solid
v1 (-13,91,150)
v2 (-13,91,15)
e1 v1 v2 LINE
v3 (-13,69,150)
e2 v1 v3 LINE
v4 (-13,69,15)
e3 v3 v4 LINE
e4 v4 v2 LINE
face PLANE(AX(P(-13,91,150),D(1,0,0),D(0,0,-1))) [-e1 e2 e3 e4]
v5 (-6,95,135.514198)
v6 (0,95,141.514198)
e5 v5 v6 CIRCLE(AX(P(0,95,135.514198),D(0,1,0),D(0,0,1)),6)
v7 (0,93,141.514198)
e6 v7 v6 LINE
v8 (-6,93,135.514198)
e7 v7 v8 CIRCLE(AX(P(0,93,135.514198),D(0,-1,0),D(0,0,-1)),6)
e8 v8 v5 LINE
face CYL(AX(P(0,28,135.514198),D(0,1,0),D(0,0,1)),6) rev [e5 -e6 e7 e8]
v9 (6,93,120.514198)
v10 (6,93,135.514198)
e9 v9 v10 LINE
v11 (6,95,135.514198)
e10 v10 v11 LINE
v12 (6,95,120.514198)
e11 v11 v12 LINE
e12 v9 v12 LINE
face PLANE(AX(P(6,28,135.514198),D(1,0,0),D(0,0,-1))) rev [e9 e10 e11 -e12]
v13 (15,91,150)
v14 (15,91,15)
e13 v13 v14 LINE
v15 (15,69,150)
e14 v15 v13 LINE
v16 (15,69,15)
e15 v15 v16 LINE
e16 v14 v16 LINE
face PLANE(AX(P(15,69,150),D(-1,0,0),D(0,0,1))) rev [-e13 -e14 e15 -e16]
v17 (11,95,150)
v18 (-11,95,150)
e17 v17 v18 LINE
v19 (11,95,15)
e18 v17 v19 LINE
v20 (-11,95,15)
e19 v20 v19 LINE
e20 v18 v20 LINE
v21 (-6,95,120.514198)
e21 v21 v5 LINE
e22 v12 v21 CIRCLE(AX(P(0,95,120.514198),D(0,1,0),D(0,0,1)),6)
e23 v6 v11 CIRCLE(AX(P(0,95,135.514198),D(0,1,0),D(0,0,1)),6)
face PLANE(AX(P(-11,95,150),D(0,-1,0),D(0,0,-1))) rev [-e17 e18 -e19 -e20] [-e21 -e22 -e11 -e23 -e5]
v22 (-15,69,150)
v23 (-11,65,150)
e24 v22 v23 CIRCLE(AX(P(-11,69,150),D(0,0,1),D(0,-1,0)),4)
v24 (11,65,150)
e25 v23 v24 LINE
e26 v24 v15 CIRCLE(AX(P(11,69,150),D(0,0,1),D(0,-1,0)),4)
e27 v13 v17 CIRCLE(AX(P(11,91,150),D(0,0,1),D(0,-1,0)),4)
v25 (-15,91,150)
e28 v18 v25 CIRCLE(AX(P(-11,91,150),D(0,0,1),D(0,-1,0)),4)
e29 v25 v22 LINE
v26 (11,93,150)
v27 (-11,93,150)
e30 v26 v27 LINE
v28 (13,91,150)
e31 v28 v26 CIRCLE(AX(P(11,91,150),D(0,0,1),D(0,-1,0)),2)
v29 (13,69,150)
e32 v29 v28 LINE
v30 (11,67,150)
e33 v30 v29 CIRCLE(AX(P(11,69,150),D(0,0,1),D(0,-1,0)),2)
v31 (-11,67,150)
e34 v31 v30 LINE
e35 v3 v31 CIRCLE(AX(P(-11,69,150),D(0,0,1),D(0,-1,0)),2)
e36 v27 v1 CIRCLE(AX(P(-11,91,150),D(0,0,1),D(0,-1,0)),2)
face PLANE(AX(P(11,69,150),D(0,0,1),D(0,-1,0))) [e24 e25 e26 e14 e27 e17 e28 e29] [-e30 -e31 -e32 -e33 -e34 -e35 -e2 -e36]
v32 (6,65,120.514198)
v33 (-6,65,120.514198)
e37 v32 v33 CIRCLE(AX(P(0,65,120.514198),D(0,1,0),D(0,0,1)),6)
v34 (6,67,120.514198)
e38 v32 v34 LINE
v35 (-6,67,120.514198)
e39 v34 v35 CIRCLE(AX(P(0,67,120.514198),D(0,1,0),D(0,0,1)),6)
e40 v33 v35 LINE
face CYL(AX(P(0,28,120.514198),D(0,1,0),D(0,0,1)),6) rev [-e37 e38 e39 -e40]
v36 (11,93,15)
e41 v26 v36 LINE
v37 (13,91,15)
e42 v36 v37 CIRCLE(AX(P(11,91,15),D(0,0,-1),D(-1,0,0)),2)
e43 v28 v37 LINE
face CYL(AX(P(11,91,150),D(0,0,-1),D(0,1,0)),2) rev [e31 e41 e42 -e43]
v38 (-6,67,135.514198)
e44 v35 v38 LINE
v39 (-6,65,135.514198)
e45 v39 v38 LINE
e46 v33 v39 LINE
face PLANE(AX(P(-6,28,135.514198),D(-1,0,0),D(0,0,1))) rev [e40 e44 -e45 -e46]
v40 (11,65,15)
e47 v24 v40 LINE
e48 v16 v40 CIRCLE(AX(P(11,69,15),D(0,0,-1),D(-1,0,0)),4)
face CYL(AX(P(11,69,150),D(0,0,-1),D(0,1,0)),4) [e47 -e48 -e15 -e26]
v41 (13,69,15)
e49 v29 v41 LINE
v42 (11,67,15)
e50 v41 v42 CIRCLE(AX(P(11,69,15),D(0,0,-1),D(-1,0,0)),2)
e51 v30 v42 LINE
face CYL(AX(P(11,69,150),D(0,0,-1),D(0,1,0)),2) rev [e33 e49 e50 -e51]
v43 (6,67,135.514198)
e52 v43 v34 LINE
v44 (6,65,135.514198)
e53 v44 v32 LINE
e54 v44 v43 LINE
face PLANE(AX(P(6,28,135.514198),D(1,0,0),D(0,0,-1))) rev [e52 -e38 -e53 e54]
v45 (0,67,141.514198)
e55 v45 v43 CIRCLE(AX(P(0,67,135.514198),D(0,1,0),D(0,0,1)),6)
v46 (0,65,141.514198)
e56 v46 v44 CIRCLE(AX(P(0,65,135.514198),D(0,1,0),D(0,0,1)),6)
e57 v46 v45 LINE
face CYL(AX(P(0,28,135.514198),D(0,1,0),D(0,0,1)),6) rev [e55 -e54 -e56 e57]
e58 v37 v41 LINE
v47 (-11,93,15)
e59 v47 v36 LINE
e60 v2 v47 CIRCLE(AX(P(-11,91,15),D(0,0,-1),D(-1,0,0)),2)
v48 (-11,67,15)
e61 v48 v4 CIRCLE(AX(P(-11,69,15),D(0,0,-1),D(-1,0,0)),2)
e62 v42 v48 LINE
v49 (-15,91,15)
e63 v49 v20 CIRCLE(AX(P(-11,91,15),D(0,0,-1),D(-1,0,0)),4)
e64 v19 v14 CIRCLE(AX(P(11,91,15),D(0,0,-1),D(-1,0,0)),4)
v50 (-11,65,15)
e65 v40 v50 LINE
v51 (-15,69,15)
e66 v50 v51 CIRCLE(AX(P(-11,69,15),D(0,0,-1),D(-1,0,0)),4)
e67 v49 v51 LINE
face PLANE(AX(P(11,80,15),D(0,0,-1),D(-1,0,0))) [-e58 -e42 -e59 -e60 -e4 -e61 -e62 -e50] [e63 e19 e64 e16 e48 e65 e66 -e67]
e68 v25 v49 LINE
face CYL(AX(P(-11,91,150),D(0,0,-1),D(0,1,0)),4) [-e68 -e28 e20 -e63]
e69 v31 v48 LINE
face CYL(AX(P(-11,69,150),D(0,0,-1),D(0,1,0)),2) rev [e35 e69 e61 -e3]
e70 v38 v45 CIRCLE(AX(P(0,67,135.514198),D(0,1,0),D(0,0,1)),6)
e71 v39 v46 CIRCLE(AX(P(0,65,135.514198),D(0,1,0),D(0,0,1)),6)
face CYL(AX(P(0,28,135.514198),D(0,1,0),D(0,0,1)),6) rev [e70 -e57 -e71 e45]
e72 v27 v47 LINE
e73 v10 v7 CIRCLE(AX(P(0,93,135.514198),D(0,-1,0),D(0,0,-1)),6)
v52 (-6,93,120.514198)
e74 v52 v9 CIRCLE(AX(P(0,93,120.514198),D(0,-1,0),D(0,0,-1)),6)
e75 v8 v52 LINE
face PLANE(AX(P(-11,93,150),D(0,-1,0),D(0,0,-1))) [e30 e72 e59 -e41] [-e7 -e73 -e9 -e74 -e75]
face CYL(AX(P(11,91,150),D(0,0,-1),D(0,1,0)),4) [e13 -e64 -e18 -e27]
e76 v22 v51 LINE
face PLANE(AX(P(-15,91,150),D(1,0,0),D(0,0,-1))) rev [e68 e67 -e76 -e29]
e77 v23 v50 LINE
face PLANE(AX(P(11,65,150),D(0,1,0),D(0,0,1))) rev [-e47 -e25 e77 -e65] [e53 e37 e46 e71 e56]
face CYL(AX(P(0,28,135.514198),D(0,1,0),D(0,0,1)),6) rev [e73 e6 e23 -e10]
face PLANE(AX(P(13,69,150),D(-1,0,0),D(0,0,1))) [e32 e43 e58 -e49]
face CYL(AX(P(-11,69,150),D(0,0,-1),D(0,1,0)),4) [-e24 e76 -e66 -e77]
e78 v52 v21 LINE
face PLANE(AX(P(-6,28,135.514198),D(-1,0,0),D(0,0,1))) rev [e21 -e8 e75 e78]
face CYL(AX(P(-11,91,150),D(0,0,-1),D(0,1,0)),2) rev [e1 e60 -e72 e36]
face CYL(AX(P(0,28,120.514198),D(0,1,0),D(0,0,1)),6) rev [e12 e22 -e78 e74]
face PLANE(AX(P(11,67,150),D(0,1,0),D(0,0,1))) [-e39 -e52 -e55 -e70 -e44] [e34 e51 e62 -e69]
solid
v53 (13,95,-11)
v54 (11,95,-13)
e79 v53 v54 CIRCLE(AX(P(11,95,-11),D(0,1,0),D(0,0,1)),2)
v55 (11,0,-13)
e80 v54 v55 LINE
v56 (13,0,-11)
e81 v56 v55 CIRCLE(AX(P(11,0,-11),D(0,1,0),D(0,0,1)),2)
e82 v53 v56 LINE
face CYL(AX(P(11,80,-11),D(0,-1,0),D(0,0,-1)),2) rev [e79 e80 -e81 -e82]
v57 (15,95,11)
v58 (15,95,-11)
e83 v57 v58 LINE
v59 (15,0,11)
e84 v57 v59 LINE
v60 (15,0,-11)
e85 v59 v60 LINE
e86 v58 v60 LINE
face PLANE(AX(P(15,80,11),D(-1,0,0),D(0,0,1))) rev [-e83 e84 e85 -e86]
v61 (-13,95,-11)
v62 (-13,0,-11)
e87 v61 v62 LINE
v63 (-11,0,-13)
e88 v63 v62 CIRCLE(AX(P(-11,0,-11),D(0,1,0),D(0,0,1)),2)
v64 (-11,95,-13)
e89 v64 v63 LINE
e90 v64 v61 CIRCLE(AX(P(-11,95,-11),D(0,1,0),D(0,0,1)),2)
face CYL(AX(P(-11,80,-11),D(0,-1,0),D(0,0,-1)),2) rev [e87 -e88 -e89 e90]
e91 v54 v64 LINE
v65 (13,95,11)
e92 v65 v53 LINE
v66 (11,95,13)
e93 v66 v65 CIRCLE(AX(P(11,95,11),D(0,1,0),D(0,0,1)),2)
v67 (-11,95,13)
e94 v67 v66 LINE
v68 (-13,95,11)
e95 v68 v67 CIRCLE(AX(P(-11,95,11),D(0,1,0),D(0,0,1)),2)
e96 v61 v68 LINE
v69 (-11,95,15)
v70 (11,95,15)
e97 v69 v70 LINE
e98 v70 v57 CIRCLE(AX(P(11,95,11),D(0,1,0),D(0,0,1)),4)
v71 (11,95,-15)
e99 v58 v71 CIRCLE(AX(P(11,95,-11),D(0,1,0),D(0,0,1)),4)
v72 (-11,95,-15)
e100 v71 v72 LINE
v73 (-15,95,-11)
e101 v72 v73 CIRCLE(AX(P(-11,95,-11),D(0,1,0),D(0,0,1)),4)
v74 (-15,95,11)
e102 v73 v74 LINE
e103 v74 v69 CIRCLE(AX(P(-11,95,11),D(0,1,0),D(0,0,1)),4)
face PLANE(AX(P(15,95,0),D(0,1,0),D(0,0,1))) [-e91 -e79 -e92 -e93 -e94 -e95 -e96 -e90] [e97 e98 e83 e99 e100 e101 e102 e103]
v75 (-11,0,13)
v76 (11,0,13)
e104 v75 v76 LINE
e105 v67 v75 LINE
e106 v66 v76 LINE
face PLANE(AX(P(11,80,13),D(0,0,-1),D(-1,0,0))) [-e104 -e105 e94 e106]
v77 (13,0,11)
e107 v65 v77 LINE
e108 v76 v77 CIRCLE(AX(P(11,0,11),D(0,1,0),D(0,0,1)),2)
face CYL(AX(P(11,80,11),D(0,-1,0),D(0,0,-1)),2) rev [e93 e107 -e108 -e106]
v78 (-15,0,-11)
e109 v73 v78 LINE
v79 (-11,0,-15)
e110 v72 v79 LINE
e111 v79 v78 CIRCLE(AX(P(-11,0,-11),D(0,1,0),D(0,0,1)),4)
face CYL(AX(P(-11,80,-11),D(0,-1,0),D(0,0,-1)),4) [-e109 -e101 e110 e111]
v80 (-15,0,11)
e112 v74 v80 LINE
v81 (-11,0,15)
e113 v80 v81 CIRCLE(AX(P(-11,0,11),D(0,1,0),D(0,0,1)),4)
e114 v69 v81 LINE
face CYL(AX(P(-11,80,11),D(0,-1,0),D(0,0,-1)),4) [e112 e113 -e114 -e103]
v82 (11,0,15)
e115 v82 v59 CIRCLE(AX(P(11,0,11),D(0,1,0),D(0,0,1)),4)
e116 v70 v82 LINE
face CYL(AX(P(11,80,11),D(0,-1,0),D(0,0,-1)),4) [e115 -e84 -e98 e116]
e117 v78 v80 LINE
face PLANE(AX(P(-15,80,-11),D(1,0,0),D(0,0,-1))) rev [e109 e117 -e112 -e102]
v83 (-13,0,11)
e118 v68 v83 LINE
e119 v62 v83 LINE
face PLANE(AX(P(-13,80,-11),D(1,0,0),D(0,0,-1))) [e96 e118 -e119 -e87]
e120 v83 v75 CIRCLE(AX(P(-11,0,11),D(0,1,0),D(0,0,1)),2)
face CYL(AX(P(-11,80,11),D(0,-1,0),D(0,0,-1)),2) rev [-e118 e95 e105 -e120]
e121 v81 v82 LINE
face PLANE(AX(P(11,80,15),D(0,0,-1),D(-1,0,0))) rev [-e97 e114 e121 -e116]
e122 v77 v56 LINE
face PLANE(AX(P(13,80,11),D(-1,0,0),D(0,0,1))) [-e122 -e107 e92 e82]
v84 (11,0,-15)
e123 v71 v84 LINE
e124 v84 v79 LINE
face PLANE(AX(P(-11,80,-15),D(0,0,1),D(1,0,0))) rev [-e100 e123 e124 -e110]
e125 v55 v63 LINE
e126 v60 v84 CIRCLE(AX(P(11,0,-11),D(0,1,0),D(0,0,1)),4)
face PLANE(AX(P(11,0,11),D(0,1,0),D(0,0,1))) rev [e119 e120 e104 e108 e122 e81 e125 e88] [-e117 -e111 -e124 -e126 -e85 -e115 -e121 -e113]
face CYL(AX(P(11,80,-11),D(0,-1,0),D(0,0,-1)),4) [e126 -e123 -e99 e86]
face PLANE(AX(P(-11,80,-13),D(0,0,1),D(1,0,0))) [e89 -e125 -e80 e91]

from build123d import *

# Parameters (mm, degrees)
GB_6728_1986_030_X_30_X_2_1_DEPTH        = 95
GB_6728_1986_030_X_30_X_2_1_2_DEPTH      = 150
GB_6728_1986_030_X_30_X_2_1_2_DEPTH_BACK = 1
CUT_EXTRUDE_1_DEPTH                      = 67


with BuildPart() as part:
    # Sketch13 on segment 1 (carried to segment 1) → Gb／6728-1986方形空心型钢 030 X 30 X 2(1) (new body)
    with BuildSketch(Plane.ZX):
        with BuildLine():
            Line((-11, -15), (11, -15))
            ThreePointArc((11, -15), (13.828427125, -13.828427125), (15, -11))
            Line((15, -11), (15, 11))
            ThreePointArc((15, 11), (13.828427125, 13.828427125), (11, 15))
            Line((11, 15), (-11, 15))
            ThreePointArc((-11, 15), (-13.828427125, 13.828427125), (-15, 11))
            Line((-15, 11), (-15, -11))
            ThreePointArc((-15, -11), (-13.828427125, -13.828427125), (-11, -15))
        make_face()
        with BuildLine():
            Line((-11, -13), (11, -13))
            ThreePointArc((11, -13), (12.414213562, -12.414213562), (13, -11))
            Line((13, -11), (13, 11))
            ThreePointArc((13, 11), (12.414213562, 12.414213562), (11, 13))
            Line((11, 13), (-11, 13))
            ThreePointArc((-11, 13), (-12.414213562, 12.414213562), (-13, 11))
            Line((-13, 11), (-13, -11))
            ThreePointArc((-13, -11), (-12.414213562, -12.414213562), (-11, -13))
        make_face(mode=Mode.SUBTRACT)
    extrude(amount=GB_6728_1986_030_X_30_X_2_1_DEPTH)


with BuildPart() as body_2:
    # Sketch13 → Gb_6728-1986_ 030 X 30 X 2_1 2 (new, two sides: drawn at the far end of the back side and taken through both)
    with BuildSketch(Plane(origin=(0, 80, 0), x_dir=(0, -1, 0), z_dir=(0, 0, 1)).offset(-GB_6728_1986_030_X_30_X_2_1_2_DEPTH_BACK)):
        with BuildLine():
            Line((-11, -15), (11, -15))
            ThreePointArc((11, -15), (13.828427125, -13.828427125), (15, -11))
            Line((15, -11), (15, 11))
            ThreePointArc((15, 11), (13.828427125, 13.828427125), (11, 15))
            Line((11, 15), (-11, 15))
            ThreePointArc((-11, 15), (-13.828427125, 13.828427125), (-15, 11))
            Line((-15, 11), (-15, -11))
            ThreePointArc((-15, -11), (-13.828427125, -13.828427125), (-11, -15))
        make_face()
        with BuildLine():
            Line((-11, -13), (11, -13))
            ThreePointArc((11, -13), (12.414213562, -12.414213562), (13, -11))
            Line((13, -11), (13, 11))
            ThreePointArc((13, 11), (12.414213562, 12.414213562), (11, 13))
            Line((11, 13), (-11, 13))
            ThreePointArc((-11, 13), (-12.414213562, 12.414213562), (-13, 11))
            Line((-13, 11), (-13, -11))
            ThreePointArc((-13, -11), (-12.414213562, -12.414213562), (-11, -13))
        make_face(mode=Mode.SUBTRACT)
    extrude(amount=GB_6728_1986_030_X_30_X_2_1_2_DEPTH + GB_6728_1986_030_X_30_X_2_1_2_DEPTH_BACK)

    # Gb_6728-1986_ 030 X 30 X 2_1 2 end butt
    split(bisect_by=Plane(origin=(0, 80, 15), x_dir=(0, -1, 0), z_dir=(0, 0, 1)), keep=Keep.TOP)

    # 草图6 → 切除-拉伸1 (cut)
    with BuildSketch(Plane(origin=(0, 95, 0), x_dir=(1, 0, 0), z_dir=(0, 1, 0))):
        with BuildLine():
            Line((-6, -135.514198409), (-6, -120.514198409))
            ThreePointArc((-6, -120.514198409), (0, -114.514198409), (6, -120.514198409))
            Line((6, -120.514198409), (6, -135.514198409))
            ThreePointArc((6, -135.514198409), (0, -141.514198409), (-6, -135.514198409))
        make_face()
    extrude(amount=-CUT_EXTRUDE_1_DEPTH, mode=Mode.SUBTRACT)


solid = Compound([part.part, body_2.part])
